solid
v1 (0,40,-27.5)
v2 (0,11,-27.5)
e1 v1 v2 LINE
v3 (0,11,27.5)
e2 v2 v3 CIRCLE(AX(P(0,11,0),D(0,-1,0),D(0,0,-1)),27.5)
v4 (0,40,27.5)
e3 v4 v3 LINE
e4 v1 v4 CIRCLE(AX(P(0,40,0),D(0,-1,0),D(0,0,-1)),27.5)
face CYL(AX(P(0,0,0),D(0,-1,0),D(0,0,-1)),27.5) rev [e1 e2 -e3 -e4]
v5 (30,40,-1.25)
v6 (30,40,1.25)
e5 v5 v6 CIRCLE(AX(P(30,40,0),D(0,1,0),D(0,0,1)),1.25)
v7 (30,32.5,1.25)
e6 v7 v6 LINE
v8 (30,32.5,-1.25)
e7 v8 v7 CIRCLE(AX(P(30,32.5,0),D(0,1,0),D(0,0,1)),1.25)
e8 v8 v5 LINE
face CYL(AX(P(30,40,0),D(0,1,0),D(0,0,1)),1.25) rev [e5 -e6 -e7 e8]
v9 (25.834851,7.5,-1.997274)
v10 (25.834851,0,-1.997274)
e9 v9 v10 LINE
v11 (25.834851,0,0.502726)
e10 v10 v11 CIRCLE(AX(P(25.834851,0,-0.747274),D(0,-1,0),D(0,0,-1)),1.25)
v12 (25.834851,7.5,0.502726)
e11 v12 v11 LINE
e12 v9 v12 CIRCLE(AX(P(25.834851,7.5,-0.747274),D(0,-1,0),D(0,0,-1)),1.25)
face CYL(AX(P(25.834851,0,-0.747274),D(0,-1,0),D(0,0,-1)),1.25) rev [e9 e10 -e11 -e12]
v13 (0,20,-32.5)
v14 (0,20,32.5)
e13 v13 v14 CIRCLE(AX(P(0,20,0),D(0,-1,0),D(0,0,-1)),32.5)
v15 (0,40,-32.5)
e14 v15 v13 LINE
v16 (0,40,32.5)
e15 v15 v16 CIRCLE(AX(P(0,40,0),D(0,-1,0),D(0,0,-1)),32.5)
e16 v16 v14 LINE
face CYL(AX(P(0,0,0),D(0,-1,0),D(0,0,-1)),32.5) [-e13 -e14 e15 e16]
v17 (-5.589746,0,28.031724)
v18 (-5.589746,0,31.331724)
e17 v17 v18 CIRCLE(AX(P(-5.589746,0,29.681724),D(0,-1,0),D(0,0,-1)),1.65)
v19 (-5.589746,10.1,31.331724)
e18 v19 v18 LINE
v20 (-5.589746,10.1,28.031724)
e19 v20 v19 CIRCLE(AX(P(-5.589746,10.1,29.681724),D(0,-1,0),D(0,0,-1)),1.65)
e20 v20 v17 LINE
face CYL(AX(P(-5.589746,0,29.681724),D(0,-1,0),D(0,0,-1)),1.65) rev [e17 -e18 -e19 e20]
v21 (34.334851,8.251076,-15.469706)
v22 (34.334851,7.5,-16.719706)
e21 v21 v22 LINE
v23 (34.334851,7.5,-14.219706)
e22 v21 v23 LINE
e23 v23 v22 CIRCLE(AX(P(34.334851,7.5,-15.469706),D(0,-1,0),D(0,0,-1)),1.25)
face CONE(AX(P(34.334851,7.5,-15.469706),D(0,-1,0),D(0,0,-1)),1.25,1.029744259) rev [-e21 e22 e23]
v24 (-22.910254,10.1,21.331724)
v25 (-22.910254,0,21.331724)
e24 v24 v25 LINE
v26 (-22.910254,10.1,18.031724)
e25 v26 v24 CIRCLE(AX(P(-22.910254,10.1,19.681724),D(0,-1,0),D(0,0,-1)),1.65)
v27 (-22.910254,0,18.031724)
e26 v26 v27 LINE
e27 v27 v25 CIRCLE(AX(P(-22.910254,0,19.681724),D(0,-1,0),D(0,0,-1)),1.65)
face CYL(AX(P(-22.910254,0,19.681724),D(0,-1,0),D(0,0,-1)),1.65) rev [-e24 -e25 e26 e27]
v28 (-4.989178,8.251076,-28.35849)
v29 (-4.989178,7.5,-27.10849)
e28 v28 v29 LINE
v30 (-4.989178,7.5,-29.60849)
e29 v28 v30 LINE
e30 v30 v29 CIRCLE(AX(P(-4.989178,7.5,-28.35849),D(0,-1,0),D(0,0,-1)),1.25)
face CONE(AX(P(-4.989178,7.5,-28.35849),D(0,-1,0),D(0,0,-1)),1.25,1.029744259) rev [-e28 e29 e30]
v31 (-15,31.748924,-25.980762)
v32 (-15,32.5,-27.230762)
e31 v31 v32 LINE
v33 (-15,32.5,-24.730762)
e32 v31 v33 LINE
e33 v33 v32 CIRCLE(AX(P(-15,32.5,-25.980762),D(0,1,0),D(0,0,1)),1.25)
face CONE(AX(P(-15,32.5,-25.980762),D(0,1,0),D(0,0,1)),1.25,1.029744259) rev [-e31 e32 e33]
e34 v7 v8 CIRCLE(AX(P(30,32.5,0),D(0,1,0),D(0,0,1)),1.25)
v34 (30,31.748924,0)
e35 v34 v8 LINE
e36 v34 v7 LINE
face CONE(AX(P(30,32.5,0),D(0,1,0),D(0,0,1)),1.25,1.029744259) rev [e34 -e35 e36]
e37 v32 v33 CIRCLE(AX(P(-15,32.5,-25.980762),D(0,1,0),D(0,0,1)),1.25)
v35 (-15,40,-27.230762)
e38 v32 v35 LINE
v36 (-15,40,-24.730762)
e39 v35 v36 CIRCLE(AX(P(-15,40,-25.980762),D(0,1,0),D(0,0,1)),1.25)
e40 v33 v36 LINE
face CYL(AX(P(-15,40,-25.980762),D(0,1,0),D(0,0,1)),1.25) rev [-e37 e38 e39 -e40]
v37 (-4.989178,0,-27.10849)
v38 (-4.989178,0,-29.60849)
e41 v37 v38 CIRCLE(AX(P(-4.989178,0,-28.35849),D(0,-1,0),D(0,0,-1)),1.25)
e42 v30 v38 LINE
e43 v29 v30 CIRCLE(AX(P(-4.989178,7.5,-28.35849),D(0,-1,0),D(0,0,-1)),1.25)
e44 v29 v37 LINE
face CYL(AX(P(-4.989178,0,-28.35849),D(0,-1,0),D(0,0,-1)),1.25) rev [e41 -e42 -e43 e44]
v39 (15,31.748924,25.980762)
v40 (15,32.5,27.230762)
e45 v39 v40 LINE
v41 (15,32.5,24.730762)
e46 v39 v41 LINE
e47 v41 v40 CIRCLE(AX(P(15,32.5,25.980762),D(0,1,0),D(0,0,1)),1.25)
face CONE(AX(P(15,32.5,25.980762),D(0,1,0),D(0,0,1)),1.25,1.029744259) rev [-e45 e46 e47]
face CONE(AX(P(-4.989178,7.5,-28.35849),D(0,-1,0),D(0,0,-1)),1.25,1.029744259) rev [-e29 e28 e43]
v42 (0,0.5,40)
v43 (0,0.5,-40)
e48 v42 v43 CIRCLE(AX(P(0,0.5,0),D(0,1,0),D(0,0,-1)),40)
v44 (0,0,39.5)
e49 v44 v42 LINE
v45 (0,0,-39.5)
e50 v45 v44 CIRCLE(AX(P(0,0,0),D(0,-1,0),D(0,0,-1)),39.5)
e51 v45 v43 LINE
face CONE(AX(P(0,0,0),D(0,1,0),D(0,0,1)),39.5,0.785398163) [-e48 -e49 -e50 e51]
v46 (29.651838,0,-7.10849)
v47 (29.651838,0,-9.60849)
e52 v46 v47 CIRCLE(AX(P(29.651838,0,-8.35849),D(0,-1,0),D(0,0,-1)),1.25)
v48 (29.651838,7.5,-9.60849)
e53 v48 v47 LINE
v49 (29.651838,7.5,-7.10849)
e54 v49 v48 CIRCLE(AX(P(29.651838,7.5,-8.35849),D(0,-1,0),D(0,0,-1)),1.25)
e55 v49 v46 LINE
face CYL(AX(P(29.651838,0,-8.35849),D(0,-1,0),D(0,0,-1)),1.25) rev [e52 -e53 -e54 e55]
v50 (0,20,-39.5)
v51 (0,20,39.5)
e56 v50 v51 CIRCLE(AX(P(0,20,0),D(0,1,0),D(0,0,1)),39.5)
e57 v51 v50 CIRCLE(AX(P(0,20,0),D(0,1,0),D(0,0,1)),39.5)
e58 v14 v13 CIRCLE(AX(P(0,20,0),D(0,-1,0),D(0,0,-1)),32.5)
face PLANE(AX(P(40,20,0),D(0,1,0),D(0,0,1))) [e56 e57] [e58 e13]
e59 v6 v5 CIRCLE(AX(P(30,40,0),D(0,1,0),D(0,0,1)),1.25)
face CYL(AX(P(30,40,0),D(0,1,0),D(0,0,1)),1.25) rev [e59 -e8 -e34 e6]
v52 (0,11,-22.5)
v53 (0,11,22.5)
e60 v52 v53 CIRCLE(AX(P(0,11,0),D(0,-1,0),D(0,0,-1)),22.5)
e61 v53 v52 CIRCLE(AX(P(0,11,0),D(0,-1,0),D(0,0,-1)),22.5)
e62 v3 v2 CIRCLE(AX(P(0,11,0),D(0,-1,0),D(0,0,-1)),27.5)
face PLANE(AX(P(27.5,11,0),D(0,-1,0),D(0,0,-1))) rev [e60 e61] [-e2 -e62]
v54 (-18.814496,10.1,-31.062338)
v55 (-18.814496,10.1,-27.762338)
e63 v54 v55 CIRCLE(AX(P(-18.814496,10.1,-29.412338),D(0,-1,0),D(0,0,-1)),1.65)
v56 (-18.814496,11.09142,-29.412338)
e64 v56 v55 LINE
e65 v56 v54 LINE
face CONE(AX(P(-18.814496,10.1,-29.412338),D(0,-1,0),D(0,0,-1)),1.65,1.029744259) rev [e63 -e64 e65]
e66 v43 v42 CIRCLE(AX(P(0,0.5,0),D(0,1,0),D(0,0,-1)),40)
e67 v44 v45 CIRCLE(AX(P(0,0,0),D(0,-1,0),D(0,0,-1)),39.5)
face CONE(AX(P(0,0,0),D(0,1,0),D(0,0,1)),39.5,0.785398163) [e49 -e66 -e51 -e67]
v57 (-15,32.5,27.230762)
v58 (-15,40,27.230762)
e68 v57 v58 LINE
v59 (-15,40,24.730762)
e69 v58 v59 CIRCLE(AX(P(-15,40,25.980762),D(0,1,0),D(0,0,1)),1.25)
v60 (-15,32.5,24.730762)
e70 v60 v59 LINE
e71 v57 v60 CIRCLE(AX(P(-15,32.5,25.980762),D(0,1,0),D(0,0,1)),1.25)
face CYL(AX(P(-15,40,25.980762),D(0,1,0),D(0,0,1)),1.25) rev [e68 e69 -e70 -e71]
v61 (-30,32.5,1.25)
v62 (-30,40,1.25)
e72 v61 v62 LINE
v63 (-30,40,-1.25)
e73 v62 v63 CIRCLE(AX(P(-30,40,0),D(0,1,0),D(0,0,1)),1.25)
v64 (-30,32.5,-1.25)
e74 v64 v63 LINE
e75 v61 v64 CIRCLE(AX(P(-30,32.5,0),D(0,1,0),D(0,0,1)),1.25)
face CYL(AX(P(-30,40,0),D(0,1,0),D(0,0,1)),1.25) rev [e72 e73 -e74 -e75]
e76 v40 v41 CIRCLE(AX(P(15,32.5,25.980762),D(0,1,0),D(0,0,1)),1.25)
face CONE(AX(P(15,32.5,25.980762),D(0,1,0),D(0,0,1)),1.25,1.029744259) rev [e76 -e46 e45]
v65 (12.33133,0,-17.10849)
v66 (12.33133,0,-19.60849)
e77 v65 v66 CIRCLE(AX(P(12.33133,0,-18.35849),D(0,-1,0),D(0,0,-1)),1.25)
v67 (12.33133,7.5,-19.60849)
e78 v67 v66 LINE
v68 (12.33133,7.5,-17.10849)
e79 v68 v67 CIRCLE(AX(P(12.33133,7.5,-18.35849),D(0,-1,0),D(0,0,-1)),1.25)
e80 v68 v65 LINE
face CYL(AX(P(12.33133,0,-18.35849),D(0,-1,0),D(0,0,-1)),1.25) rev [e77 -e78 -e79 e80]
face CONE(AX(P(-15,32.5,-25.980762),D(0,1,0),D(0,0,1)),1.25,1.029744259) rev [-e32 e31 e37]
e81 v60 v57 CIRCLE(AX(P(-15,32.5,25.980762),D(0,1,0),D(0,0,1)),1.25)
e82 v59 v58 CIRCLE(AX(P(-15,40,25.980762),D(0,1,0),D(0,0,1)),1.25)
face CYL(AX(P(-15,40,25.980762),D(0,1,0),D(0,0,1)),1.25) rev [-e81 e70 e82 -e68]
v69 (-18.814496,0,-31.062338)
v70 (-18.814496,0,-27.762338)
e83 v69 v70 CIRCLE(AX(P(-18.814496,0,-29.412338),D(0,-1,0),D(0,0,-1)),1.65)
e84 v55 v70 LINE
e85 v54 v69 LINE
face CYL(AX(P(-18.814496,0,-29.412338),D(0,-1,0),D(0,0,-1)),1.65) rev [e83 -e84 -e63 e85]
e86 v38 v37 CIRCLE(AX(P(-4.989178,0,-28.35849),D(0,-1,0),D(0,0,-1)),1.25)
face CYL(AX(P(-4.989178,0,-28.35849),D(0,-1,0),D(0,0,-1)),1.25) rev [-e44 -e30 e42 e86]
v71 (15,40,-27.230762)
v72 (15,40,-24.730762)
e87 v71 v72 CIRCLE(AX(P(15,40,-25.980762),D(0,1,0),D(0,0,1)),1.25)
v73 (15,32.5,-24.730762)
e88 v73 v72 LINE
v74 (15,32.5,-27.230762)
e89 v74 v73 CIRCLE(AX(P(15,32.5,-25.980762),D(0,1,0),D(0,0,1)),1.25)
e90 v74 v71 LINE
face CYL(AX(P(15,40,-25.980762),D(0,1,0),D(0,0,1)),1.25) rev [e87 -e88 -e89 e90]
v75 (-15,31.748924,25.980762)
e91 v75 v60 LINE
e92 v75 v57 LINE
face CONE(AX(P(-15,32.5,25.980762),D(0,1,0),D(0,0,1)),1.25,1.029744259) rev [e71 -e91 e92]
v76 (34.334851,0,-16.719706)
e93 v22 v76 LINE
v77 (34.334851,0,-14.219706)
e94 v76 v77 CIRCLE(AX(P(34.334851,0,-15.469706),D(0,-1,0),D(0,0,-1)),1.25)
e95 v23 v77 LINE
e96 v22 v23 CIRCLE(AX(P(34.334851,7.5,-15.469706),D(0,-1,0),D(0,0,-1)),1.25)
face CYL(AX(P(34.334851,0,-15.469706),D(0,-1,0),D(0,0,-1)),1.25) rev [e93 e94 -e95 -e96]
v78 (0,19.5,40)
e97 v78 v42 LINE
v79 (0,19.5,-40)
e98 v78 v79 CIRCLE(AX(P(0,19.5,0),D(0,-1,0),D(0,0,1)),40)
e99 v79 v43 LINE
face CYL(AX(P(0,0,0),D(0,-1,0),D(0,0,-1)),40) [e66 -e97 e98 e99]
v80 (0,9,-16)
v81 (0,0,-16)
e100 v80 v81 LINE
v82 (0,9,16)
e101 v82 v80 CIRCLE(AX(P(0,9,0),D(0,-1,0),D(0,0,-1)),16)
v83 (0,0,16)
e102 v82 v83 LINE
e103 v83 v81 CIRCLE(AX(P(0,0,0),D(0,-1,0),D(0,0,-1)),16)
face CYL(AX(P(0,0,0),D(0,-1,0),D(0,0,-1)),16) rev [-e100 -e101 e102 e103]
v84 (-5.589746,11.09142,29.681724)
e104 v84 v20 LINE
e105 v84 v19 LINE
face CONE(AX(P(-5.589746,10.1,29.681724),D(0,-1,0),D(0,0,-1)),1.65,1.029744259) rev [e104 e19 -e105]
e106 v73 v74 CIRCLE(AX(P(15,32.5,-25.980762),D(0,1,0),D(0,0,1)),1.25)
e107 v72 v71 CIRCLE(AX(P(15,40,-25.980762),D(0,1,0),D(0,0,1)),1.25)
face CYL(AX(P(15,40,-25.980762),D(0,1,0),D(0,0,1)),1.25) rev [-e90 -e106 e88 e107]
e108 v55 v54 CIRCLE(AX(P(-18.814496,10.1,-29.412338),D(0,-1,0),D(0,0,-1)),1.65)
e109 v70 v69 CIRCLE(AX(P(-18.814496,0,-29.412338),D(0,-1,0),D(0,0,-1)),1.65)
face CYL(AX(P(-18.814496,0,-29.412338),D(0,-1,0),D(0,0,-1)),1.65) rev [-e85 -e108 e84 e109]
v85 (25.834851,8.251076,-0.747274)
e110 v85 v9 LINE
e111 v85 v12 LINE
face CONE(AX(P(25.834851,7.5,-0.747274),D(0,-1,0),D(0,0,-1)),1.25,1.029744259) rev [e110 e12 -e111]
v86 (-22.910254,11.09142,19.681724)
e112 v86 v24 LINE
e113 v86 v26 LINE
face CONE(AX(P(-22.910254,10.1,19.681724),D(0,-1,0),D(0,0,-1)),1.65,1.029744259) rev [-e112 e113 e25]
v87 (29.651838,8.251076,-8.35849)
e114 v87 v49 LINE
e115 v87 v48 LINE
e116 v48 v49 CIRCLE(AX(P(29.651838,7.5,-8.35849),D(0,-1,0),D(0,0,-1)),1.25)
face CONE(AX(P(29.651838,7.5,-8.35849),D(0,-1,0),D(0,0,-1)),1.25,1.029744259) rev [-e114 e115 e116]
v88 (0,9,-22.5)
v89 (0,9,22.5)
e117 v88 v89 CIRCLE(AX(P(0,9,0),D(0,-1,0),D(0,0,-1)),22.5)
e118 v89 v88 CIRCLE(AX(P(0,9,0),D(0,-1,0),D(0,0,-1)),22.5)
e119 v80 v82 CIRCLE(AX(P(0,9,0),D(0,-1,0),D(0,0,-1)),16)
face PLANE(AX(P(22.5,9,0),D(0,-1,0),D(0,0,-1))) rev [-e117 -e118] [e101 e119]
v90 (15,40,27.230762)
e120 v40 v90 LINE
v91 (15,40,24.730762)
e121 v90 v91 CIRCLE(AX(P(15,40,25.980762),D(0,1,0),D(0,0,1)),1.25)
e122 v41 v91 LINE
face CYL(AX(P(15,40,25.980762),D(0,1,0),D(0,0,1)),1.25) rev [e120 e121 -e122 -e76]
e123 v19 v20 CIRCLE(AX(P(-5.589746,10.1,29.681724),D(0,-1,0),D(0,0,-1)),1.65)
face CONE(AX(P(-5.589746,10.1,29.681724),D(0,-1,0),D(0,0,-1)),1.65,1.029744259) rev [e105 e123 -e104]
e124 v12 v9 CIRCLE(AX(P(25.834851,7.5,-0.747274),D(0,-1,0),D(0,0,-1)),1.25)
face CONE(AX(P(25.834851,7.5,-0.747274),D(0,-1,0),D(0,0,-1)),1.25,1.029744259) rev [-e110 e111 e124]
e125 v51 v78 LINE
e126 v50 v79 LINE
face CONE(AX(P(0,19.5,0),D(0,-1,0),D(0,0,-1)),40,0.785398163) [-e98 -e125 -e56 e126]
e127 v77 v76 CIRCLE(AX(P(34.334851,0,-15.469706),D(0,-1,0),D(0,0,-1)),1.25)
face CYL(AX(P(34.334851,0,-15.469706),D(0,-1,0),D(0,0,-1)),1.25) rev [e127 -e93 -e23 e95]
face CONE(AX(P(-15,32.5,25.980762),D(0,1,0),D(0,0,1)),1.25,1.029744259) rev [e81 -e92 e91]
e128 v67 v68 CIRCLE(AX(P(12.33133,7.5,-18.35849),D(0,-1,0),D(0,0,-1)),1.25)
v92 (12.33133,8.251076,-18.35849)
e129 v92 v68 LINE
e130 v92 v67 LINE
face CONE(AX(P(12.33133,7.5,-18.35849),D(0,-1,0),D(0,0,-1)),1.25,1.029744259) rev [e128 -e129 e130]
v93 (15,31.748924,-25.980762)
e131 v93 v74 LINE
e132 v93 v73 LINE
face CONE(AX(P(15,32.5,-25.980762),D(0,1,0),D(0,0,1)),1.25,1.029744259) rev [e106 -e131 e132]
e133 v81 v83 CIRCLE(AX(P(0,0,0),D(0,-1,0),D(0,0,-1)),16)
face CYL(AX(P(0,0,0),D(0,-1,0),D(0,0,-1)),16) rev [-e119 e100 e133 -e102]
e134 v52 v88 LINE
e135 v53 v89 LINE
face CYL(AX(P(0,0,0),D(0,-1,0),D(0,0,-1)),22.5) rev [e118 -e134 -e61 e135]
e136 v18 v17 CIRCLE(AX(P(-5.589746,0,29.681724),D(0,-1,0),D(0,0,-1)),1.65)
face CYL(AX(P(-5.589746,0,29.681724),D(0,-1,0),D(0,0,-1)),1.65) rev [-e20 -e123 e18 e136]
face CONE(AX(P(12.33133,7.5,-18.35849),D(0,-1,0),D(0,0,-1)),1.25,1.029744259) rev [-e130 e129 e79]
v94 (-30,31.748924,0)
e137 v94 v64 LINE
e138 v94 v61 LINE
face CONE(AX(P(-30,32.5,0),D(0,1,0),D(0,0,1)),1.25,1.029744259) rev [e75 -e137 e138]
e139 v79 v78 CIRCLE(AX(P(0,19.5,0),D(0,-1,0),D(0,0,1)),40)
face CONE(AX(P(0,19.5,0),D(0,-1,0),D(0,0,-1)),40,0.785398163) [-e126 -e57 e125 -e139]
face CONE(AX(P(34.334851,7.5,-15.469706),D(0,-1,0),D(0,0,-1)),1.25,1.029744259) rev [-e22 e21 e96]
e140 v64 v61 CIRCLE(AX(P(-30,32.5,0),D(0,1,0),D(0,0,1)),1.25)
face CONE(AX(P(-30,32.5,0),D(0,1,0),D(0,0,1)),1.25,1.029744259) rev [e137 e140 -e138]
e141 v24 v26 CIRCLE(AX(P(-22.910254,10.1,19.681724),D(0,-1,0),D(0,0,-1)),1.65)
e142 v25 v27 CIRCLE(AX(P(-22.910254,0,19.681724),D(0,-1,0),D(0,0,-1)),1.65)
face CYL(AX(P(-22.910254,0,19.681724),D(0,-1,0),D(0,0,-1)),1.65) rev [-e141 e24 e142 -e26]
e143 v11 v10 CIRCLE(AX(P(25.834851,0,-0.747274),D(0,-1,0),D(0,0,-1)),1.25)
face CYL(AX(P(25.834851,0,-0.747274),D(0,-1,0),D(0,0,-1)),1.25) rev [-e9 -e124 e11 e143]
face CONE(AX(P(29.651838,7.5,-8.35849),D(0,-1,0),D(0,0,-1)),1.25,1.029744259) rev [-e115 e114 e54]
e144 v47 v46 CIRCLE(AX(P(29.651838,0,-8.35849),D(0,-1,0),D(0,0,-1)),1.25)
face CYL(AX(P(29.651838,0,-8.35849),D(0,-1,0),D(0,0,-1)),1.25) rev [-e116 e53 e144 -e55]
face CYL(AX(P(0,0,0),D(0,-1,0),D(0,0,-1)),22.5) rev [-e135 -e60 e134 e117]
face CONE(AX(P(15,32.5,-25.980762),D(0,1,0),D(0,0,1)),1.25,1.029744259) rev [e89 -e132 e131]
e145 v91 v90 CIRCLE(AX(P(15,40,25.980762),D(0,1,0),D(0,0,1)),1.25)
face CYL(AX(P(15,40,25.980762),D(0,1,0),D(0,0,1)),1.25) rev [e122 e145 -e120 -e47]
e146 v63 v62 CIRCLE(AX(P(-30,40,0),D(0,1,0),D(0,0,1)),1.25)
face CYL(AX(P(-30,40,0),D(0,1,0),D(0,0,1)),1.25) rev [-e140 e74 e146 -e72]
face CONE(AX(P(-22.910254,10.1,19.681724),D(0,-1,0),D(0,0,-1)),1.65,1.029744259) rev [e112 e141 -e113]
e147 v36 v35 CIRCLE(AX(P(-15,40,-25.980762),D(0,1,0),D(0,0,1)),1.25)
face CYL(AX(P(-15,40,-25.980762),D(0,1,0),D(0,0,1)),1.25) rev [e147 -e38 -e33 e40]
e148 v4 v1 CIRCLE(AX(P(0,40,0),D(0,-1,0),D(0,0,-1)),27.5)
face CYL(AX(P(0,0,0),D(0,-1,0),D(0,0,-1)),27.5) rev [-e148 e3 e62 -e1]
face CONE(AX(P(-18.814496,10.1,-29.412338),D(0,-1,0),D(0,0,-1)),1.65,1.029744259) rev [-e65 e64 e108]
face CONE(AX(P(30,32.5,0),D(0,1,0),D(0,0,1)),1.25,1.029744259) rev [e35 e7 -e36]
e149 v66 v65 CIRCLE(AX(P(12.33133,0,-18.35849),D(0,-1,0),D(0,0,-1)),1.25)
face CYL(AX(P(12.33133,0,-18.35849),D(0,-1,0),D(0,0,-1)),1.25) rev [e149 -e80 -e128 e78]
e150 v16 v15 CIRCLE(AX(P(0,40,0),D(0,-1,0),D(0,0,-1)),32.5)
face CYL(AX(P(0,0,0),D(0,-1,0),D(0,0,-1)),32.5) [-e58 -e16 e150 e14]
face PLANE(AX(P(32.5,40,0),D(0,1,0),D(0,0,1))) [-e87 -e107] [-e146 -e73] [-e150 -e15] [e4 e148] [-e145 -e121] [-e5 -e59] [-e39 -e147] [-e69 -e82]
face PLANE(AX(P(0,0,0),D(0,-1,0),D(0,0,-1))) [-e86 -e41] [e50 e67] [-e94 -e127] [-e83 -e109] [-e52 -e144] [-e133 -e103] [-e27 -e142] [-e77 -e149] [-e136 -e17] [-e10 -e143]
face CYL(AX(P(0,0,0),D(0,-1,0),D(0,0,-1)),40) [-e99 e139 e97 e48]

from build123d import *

# Parameters (mm, degrees)
M3_TAPPED_HOLE1_D     = 2.5
M3_TAPPED_HOLE1_DEPTH = 7.5
M3_TAPPED_HOLE1_TIP   = 0.751075774
CHAMFER1_SIZE         = 0.5
M4_TAPPED_HOLE1_D     = 3.3
M4_TAPPED_HOLE1_DEPTH = 10.1
M4_TAPPED_HOLE1_TIP   = 0.991420021
M3_TAPPED_HOLE2_D     = 2.5
M3_TAPPED_HOLE2_DEPTH = 7.5
M3_TAPPED_HOLE2_TIP   = 0.751075774
M3_TAPPED_HOLE3_D     = 2.5
M3_TAPPED_HOLE3_DEPTH = 7.5
M3_TAPPED_HOLE3_TIP   = 0.751075774
M4_TAPPED_HOLE2_D     = 3.3
M4_TAPPED_HOLE2_DEPTH = 10.1
M4_TAPPED_HOLE2_TIP   = 0.991420021


with BuildPart() as part:
    # Sketch1 → Revolve1 (revolve)
    with BuildSketch(Plane.XY, mode=Mode.PRIVATE) as revolve1_sk:
        Polygon((0, 0), (40, 0), (40, 20), (32.5, 20), (32.5, 40), (0, 40), align=None)
    revolve(revolve1_sk.sketch.rotate(Axis((0, 0, 0), (0, 1, 0)), 90), axis=Axis((0, 0, 0), (0, 1, 0)))

    # Sketch2 → Cut-Revolve1 (revolve, cut)
    with BuildSketch(Plane.XY, mode=Mode.PRIVATE) as cut_revolve1_sk:
        Polygon((0, 40), (27.5, 40), (27.5, 11), (22.5, 11), (22.5, 9), (16, 9), (16, 0), (0, 0), align=None)
    revolve(cut_revolve1_sk.sketch.rotate(Axis((0, 0, 0), (0, 1, 0)), 90), axis=Axis((0, 0, 0), (0, 1, 0)), mode=Mode.SUBTRACT)

    # M3 Tapped Hole1
    with Locations(Plane(origin=(0, 40, 0), x_dir=(1, 0, 0), z_dir=(0, 1, 0))):
        with Locations((-30, 0), (-15, 25.980762114), (15, 25.980762114), (30, 0), (15, -25.980762114), (-15, -25.980762114), (0, 0)):
            Hole(M3_TAPPED_HOLE1_D / 2, depth=M3_TAPPED_HOLE1_DEPTH)
            with Locations((0, 0, -(M3_TAPPED_HOLE1_DEPTH + M3_TAPPED_HOLE1_TIP / 2))):  # 118° drill point
                Cone(0, M3_TAPPED_HOLE1_D / 2, M3_TAPPED_HOLE1_TIP, mode=Mode.SUBTRACT)

    # Chamfer1
    chamfer1_edges = [part.edges().sort_by_distance(p)[0] for p in [
        (0, 0, 40),
        (0, 20, 40),
    ]]
    chamfer(chamfer1_edges, length=CHAMFER1_SIZE)

    # M4 Tapped Hole1
    with Locations(Plane(origin=(0, 0, 0), x_dir=(-1, 0, 0), z_dir=(0, -1, 0))):
        with Locations((18.814495684, 29.412337557)):
            Hole(M4_TAPPED_HOLE1_D / 2, depth=M4_TAPPED_HOLE1_DEPTH)
            with Locations((0, 0, -(M4_TAPPED_HOLE1_DEPTH + M4_TAPPED_HOLE1_TIP / 2))):  # 118° drill point
                Cone(0, M4_TAPPED_HOLE1_D / 2, M4_TAPPED_HOLE1_TIP, mode=Mode.SUBTRACT)

    # M3 Tapped Hole2
    with Locations(Plane(origin=(0, 0, 0), x_dir=(-1, 0, 0), z_dir=(0, -1, 0))):
        with Locations((-34.334850717, 15.469705912), (-25.834850717, 0.747274048)):
            Hole(M3_TAPPED_HOLE2_D / 2, depth=M3_TAPPED_HOLE2_DEPTH)
            with Locations((0, 0, -(M3_TAPPED_HOLE2_DEPTH + M3_TAPPED_HOLE2_TIP / 2))):  # 118° drill point
                Cone(0, M3_TAPPED_HOLE2_D / 2, M3_TAPPED_HOLE2_TIP, mode=Mode.SUBTRACT)

    # M3 Tapped Hole3
    with Locations(Plane(origin=(0, 0, 0), x_dir=(-1, 0, 0), z_dir=(0, -1, 0))):
        with Locations((4.989178136, 28.35848998), (-12.331329939, 18.35848998), (-29.651838015, 8.35848998)):
            Hole(M3_TAPPED_HOLE3_D / 2, depth=M3_TAPPED_HOLE3_DEPTH)
            with Locations((0, 0, -(M3_TAPPED_HOLE3_DEPTH + M3_TAPPED_HOLE3_TIP / 2))):  # 118° drill point
                Cone(0, M3_TAPPED_HOLE3_D / 2, M3_TAPPED_HOLE3_TIP, mode=Mode.SUBTRACT)

    # M4 Tapped Hole2
    with Locations(Plane(origin=(0, 0, 0), x_dir=(-1, 0, 0), z_dir=(0, -1, 0))):
        with Locations((22.910254038, -19.681724008), (5.589745962, -29.681724008)):
            Hole(M4_TAPPED_HOLE2_D / 2, depth=M4_TAPPED_HOLE2_DEPTH)
            with Locations((0, 0, -(M4_TAPPED_HOLE2_DEPTH + M4_TAPPED_HOLE2_TIP / 2))):  # 118° drill point
                Cone(0, M4_TAPPED_HOLE2_D / 2, M4_TAPPED_HOLE2_TIP, mode=Mode.SUBTRACT)


solid = part.part
